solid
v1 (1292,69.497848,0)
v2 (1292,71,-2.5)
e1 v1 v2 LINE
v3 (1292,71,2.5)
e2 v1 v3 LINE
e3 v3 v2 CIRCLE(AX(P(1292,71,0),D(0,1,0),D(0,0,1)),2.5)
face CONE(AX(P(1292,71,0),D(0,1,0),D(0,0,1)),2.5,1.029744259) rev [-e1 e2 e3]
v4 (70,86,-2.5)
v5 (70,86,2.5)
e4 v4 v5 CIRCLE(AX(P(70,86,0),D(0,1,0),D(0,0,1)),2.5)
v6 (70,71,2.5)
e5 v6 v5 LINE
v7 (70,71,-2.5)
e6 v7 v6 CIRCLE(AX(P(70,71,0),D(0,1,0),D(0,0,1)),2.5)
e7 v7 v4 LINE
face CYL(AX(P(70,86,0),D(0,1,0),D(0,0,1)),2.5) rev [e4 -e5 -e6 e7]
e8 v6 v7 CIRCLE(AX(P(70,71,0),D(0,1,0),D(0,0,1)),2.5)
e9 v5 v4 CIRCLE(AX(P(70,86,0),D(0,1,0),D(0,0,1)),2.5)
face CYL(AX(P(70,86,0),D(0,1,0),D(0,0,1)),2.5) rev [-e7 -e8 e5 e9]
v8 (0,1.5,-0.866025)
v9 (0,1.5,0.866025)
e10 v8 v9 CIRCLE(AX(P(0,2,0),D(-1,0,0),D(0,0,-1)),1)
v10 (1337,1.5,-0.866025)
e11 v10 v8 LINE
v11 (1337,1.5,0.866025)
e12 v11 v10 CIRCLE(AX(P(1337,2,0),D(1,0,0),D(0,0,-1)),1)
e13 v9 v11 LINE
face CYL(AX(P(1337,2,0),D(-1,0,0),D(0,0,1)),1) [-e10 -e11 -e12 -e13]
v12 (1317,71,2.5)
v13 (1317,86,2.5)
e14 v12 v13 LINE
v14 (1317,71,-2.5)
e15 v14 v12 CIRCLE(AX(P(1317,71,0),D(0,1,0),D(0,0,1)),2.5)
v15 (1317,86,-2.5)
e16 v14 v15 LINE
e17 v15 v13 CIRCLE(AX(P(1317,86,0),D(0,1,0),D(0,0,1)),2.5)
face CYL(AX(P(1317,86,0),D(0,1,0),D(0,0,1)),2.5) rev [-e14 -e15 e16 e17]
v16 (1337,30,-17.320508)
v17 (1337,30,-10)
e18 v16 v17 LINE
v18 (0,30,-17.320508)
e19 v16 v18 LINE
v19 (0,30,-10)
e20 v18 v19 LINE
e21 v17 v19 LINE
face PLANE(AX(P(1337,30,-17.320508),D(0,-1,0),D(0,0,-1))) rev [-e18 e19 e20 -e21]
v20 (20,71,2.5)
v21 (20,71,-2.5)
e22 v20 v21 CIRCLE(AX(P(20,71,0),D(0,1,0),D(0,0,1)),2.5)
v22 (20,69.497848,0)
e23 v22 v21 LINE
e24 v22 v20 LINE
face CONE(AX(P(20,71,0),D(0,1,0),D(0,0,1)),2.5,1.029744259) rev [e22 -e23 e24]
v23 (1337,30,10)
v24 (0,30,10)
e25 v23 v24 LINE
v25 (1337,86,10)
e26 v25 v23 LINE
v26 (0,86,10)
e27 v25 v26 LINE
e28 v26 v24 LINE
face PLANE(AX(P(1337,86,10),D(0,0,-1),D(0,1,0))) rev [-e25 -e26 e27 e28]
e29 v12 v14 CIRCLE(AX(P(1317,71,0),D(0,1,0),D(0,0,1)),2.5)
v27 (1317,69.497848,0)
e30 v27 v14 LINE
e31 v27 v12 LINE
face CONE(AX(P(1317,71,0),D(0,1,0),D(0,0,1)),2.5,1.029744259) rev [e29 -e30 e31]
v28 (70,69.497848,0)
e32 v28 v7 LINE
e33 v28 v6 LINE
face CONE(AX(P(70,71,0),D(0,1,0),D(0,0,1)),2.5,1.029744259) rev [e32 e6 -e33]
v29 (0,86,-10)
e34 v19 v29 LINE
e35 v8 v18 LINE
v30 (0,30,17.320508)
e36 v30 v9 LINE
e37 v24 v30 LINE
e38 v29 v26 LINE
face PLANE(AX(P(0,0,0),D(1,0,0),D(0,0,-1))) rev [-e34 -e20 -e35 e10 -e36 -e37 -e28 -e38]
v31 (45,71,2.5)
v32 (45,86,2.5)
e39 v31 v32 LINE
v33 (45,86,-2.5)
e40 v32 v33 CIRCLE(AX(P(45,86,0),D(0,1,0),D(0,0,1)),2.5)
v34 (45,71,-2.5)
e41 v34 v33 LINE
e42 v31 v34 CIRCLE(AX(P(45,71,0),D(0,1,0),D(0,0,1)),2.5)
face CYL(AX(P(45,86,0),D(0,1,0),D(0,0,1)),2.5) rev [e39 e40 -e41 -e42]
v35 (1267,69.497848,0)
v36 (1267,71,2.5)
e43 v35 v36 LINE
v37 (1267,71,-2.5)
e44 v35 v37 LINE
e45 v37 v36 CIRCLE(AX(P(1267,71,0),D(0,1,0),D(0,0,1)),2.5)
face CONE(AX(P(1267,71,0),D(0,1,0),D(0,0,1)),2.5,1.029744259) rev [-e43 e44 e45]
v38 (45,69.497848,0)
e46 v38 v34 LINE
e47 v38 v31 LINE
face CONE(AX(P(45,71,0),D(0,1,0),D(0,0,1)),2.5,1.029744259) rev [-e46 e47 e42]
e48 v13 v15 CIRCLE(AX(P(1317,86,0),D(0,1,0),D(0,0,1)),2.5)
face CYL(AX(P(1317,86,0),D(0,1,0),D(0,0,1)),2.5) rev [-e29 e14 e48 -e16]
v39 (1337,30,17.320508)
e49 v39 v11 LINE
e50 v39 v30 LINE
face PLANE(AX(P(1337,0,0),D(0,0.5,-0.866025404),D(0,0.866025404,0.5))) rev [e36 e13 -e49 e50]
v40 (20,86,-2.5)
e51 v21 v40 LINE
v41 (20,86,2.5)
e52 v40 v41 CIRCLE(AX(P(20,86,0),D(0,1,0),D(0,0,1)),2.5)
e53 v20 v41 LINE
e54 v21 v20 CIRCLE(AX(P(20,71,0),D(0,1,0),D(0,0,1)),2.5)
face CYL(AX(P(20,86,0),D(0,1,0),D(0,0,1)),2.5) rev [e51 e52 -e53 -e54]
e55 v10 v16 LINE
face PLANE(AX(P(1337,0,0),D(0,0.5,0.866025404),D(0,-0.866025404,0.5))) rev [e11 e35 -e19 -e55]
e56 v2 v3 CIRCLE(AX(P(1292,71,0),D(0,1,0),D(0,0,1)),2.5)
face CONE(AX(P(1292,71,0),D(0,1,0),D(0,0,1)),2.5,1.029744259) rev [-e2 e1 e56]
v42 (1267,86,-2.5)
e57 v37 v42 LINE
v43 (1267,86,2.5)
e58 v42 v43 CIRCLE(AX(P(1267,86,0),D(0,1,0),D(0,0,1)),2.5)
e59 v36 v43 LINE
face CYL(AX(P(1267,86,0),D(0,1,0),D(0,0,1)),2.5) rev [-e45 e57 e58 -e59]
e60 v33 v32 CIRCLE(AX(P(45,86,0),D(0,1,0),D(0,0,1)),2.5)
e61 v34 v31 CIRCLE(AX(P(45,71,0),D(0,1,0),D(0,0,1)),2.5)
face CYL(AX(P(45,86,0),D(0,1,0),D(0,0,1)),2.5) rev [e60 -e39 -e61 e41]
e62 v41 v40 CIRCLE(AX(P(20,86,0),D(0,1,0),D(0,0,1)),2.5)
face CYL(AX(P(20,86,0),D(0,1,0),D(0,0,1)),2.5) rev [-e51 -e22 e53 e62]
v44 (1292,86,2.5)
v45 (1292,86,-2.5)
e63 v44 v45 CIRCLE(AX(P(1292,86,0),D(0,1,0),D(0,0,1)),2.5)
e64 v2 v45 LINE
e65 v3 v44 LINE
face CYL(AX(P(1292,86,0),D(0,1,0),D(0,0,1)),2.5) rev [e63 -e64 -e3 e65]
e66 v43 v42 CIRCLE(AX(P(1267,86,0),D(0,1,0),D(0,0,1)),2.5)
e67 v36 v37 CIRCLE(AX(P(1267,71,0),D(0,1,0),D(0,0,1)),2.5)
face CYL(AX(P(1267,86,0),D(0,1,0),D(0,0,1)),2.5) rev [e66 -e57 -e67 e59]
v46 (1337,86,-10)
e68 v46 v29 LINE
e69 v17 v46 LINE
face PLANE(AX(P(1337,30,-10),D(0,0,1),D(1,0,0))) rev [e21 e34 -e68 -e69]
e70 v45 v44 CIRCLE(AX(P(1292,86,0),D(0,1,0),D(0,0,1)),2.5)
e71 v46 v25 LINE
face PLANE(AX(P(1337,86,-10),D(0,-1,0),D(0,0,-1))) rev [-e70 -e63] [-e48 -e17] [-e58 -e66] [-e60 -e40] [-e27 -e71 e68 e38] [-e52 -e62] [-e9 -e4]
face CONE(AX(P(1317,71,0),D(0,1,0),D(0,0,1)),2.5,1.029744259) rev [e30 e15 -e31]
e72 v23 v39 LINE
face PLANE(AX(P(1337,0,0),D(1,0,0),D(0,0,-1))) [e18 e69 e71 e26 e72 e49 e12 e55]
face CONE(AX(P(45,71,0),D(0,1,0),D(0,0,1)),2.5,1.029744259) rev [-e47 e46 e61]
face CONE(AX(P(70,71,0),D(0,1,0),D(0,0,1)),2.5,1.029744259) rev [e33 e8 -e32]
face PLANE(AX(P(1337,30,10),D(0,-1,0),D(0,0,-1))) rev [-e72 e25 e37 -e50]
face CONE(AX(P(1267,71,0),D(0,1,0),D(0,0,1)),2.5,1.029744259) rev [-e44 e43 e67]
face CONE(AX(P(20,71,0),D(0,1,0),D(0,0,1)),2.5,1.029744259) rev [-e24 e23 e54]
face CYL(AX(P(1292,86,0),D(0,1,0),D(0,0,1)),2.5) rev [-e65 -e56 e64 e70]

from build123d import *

# Parameters (mm, degrees)
EXTRUDE_1_DEPTH        = 1337
FILLET_1_R             = 1
HOLE_WIZARD_M6_1_D     = 5
HOLE_WIZARD_M6_1_DEPTH = 15
HOLE_WIZARD_M6_1_TIP   = 1.502151548


with BuildPart() as part:
    # 草图1 → 凸台-拉伸1 (new body)
    with BuildSketch(Plane(origin=(0, 0, 0), x_dir=(0, 0, -1), z_dir=(1, 0, 0))):
        Polygon((0, 0), (-17.320508076, 30), (-10, 30), (-10, 86), (10, 86), (10, 30), (17.320508076, 30), align=None)
    extrude(amount=EXTRUDE_1_DEPTH)

    # 圆角1
    fillet_1_edges = [part.edges().sort_by_distance(p)[0] for p in [
        (668.5, 0, 0),
    ]]
    fillet(fillet_1_edges, radius=FILLET_1_R)

    # M6 螺纹孔1
    with Locations(Plane(origin=(0, 86, 0), x_dir=(1, 0, 0), z_dir=(0, 1, 0))):
        with Locations((20, 0), (45, 0), (70, 0), (1317, 0), (1292, 0), (1267, 0)):
            Hole(HOLE_WIZARD_M6_1_D / 2, depth=HOLE_WIZARD_M6_1_DEPTH)
            with Locations((0, 0, -(HOLE_WIZARD_M6_1_DEPTH + HOLE_WIZARD_M6_1_TIP / 2))):  # 118° drill point
                Cone(0, HOLE_WIZARD_M6_1_D / 2, HOLE_WIZARD_M6_1_TIP, mode=Mode.SUBTRACT)


solid = part.part
